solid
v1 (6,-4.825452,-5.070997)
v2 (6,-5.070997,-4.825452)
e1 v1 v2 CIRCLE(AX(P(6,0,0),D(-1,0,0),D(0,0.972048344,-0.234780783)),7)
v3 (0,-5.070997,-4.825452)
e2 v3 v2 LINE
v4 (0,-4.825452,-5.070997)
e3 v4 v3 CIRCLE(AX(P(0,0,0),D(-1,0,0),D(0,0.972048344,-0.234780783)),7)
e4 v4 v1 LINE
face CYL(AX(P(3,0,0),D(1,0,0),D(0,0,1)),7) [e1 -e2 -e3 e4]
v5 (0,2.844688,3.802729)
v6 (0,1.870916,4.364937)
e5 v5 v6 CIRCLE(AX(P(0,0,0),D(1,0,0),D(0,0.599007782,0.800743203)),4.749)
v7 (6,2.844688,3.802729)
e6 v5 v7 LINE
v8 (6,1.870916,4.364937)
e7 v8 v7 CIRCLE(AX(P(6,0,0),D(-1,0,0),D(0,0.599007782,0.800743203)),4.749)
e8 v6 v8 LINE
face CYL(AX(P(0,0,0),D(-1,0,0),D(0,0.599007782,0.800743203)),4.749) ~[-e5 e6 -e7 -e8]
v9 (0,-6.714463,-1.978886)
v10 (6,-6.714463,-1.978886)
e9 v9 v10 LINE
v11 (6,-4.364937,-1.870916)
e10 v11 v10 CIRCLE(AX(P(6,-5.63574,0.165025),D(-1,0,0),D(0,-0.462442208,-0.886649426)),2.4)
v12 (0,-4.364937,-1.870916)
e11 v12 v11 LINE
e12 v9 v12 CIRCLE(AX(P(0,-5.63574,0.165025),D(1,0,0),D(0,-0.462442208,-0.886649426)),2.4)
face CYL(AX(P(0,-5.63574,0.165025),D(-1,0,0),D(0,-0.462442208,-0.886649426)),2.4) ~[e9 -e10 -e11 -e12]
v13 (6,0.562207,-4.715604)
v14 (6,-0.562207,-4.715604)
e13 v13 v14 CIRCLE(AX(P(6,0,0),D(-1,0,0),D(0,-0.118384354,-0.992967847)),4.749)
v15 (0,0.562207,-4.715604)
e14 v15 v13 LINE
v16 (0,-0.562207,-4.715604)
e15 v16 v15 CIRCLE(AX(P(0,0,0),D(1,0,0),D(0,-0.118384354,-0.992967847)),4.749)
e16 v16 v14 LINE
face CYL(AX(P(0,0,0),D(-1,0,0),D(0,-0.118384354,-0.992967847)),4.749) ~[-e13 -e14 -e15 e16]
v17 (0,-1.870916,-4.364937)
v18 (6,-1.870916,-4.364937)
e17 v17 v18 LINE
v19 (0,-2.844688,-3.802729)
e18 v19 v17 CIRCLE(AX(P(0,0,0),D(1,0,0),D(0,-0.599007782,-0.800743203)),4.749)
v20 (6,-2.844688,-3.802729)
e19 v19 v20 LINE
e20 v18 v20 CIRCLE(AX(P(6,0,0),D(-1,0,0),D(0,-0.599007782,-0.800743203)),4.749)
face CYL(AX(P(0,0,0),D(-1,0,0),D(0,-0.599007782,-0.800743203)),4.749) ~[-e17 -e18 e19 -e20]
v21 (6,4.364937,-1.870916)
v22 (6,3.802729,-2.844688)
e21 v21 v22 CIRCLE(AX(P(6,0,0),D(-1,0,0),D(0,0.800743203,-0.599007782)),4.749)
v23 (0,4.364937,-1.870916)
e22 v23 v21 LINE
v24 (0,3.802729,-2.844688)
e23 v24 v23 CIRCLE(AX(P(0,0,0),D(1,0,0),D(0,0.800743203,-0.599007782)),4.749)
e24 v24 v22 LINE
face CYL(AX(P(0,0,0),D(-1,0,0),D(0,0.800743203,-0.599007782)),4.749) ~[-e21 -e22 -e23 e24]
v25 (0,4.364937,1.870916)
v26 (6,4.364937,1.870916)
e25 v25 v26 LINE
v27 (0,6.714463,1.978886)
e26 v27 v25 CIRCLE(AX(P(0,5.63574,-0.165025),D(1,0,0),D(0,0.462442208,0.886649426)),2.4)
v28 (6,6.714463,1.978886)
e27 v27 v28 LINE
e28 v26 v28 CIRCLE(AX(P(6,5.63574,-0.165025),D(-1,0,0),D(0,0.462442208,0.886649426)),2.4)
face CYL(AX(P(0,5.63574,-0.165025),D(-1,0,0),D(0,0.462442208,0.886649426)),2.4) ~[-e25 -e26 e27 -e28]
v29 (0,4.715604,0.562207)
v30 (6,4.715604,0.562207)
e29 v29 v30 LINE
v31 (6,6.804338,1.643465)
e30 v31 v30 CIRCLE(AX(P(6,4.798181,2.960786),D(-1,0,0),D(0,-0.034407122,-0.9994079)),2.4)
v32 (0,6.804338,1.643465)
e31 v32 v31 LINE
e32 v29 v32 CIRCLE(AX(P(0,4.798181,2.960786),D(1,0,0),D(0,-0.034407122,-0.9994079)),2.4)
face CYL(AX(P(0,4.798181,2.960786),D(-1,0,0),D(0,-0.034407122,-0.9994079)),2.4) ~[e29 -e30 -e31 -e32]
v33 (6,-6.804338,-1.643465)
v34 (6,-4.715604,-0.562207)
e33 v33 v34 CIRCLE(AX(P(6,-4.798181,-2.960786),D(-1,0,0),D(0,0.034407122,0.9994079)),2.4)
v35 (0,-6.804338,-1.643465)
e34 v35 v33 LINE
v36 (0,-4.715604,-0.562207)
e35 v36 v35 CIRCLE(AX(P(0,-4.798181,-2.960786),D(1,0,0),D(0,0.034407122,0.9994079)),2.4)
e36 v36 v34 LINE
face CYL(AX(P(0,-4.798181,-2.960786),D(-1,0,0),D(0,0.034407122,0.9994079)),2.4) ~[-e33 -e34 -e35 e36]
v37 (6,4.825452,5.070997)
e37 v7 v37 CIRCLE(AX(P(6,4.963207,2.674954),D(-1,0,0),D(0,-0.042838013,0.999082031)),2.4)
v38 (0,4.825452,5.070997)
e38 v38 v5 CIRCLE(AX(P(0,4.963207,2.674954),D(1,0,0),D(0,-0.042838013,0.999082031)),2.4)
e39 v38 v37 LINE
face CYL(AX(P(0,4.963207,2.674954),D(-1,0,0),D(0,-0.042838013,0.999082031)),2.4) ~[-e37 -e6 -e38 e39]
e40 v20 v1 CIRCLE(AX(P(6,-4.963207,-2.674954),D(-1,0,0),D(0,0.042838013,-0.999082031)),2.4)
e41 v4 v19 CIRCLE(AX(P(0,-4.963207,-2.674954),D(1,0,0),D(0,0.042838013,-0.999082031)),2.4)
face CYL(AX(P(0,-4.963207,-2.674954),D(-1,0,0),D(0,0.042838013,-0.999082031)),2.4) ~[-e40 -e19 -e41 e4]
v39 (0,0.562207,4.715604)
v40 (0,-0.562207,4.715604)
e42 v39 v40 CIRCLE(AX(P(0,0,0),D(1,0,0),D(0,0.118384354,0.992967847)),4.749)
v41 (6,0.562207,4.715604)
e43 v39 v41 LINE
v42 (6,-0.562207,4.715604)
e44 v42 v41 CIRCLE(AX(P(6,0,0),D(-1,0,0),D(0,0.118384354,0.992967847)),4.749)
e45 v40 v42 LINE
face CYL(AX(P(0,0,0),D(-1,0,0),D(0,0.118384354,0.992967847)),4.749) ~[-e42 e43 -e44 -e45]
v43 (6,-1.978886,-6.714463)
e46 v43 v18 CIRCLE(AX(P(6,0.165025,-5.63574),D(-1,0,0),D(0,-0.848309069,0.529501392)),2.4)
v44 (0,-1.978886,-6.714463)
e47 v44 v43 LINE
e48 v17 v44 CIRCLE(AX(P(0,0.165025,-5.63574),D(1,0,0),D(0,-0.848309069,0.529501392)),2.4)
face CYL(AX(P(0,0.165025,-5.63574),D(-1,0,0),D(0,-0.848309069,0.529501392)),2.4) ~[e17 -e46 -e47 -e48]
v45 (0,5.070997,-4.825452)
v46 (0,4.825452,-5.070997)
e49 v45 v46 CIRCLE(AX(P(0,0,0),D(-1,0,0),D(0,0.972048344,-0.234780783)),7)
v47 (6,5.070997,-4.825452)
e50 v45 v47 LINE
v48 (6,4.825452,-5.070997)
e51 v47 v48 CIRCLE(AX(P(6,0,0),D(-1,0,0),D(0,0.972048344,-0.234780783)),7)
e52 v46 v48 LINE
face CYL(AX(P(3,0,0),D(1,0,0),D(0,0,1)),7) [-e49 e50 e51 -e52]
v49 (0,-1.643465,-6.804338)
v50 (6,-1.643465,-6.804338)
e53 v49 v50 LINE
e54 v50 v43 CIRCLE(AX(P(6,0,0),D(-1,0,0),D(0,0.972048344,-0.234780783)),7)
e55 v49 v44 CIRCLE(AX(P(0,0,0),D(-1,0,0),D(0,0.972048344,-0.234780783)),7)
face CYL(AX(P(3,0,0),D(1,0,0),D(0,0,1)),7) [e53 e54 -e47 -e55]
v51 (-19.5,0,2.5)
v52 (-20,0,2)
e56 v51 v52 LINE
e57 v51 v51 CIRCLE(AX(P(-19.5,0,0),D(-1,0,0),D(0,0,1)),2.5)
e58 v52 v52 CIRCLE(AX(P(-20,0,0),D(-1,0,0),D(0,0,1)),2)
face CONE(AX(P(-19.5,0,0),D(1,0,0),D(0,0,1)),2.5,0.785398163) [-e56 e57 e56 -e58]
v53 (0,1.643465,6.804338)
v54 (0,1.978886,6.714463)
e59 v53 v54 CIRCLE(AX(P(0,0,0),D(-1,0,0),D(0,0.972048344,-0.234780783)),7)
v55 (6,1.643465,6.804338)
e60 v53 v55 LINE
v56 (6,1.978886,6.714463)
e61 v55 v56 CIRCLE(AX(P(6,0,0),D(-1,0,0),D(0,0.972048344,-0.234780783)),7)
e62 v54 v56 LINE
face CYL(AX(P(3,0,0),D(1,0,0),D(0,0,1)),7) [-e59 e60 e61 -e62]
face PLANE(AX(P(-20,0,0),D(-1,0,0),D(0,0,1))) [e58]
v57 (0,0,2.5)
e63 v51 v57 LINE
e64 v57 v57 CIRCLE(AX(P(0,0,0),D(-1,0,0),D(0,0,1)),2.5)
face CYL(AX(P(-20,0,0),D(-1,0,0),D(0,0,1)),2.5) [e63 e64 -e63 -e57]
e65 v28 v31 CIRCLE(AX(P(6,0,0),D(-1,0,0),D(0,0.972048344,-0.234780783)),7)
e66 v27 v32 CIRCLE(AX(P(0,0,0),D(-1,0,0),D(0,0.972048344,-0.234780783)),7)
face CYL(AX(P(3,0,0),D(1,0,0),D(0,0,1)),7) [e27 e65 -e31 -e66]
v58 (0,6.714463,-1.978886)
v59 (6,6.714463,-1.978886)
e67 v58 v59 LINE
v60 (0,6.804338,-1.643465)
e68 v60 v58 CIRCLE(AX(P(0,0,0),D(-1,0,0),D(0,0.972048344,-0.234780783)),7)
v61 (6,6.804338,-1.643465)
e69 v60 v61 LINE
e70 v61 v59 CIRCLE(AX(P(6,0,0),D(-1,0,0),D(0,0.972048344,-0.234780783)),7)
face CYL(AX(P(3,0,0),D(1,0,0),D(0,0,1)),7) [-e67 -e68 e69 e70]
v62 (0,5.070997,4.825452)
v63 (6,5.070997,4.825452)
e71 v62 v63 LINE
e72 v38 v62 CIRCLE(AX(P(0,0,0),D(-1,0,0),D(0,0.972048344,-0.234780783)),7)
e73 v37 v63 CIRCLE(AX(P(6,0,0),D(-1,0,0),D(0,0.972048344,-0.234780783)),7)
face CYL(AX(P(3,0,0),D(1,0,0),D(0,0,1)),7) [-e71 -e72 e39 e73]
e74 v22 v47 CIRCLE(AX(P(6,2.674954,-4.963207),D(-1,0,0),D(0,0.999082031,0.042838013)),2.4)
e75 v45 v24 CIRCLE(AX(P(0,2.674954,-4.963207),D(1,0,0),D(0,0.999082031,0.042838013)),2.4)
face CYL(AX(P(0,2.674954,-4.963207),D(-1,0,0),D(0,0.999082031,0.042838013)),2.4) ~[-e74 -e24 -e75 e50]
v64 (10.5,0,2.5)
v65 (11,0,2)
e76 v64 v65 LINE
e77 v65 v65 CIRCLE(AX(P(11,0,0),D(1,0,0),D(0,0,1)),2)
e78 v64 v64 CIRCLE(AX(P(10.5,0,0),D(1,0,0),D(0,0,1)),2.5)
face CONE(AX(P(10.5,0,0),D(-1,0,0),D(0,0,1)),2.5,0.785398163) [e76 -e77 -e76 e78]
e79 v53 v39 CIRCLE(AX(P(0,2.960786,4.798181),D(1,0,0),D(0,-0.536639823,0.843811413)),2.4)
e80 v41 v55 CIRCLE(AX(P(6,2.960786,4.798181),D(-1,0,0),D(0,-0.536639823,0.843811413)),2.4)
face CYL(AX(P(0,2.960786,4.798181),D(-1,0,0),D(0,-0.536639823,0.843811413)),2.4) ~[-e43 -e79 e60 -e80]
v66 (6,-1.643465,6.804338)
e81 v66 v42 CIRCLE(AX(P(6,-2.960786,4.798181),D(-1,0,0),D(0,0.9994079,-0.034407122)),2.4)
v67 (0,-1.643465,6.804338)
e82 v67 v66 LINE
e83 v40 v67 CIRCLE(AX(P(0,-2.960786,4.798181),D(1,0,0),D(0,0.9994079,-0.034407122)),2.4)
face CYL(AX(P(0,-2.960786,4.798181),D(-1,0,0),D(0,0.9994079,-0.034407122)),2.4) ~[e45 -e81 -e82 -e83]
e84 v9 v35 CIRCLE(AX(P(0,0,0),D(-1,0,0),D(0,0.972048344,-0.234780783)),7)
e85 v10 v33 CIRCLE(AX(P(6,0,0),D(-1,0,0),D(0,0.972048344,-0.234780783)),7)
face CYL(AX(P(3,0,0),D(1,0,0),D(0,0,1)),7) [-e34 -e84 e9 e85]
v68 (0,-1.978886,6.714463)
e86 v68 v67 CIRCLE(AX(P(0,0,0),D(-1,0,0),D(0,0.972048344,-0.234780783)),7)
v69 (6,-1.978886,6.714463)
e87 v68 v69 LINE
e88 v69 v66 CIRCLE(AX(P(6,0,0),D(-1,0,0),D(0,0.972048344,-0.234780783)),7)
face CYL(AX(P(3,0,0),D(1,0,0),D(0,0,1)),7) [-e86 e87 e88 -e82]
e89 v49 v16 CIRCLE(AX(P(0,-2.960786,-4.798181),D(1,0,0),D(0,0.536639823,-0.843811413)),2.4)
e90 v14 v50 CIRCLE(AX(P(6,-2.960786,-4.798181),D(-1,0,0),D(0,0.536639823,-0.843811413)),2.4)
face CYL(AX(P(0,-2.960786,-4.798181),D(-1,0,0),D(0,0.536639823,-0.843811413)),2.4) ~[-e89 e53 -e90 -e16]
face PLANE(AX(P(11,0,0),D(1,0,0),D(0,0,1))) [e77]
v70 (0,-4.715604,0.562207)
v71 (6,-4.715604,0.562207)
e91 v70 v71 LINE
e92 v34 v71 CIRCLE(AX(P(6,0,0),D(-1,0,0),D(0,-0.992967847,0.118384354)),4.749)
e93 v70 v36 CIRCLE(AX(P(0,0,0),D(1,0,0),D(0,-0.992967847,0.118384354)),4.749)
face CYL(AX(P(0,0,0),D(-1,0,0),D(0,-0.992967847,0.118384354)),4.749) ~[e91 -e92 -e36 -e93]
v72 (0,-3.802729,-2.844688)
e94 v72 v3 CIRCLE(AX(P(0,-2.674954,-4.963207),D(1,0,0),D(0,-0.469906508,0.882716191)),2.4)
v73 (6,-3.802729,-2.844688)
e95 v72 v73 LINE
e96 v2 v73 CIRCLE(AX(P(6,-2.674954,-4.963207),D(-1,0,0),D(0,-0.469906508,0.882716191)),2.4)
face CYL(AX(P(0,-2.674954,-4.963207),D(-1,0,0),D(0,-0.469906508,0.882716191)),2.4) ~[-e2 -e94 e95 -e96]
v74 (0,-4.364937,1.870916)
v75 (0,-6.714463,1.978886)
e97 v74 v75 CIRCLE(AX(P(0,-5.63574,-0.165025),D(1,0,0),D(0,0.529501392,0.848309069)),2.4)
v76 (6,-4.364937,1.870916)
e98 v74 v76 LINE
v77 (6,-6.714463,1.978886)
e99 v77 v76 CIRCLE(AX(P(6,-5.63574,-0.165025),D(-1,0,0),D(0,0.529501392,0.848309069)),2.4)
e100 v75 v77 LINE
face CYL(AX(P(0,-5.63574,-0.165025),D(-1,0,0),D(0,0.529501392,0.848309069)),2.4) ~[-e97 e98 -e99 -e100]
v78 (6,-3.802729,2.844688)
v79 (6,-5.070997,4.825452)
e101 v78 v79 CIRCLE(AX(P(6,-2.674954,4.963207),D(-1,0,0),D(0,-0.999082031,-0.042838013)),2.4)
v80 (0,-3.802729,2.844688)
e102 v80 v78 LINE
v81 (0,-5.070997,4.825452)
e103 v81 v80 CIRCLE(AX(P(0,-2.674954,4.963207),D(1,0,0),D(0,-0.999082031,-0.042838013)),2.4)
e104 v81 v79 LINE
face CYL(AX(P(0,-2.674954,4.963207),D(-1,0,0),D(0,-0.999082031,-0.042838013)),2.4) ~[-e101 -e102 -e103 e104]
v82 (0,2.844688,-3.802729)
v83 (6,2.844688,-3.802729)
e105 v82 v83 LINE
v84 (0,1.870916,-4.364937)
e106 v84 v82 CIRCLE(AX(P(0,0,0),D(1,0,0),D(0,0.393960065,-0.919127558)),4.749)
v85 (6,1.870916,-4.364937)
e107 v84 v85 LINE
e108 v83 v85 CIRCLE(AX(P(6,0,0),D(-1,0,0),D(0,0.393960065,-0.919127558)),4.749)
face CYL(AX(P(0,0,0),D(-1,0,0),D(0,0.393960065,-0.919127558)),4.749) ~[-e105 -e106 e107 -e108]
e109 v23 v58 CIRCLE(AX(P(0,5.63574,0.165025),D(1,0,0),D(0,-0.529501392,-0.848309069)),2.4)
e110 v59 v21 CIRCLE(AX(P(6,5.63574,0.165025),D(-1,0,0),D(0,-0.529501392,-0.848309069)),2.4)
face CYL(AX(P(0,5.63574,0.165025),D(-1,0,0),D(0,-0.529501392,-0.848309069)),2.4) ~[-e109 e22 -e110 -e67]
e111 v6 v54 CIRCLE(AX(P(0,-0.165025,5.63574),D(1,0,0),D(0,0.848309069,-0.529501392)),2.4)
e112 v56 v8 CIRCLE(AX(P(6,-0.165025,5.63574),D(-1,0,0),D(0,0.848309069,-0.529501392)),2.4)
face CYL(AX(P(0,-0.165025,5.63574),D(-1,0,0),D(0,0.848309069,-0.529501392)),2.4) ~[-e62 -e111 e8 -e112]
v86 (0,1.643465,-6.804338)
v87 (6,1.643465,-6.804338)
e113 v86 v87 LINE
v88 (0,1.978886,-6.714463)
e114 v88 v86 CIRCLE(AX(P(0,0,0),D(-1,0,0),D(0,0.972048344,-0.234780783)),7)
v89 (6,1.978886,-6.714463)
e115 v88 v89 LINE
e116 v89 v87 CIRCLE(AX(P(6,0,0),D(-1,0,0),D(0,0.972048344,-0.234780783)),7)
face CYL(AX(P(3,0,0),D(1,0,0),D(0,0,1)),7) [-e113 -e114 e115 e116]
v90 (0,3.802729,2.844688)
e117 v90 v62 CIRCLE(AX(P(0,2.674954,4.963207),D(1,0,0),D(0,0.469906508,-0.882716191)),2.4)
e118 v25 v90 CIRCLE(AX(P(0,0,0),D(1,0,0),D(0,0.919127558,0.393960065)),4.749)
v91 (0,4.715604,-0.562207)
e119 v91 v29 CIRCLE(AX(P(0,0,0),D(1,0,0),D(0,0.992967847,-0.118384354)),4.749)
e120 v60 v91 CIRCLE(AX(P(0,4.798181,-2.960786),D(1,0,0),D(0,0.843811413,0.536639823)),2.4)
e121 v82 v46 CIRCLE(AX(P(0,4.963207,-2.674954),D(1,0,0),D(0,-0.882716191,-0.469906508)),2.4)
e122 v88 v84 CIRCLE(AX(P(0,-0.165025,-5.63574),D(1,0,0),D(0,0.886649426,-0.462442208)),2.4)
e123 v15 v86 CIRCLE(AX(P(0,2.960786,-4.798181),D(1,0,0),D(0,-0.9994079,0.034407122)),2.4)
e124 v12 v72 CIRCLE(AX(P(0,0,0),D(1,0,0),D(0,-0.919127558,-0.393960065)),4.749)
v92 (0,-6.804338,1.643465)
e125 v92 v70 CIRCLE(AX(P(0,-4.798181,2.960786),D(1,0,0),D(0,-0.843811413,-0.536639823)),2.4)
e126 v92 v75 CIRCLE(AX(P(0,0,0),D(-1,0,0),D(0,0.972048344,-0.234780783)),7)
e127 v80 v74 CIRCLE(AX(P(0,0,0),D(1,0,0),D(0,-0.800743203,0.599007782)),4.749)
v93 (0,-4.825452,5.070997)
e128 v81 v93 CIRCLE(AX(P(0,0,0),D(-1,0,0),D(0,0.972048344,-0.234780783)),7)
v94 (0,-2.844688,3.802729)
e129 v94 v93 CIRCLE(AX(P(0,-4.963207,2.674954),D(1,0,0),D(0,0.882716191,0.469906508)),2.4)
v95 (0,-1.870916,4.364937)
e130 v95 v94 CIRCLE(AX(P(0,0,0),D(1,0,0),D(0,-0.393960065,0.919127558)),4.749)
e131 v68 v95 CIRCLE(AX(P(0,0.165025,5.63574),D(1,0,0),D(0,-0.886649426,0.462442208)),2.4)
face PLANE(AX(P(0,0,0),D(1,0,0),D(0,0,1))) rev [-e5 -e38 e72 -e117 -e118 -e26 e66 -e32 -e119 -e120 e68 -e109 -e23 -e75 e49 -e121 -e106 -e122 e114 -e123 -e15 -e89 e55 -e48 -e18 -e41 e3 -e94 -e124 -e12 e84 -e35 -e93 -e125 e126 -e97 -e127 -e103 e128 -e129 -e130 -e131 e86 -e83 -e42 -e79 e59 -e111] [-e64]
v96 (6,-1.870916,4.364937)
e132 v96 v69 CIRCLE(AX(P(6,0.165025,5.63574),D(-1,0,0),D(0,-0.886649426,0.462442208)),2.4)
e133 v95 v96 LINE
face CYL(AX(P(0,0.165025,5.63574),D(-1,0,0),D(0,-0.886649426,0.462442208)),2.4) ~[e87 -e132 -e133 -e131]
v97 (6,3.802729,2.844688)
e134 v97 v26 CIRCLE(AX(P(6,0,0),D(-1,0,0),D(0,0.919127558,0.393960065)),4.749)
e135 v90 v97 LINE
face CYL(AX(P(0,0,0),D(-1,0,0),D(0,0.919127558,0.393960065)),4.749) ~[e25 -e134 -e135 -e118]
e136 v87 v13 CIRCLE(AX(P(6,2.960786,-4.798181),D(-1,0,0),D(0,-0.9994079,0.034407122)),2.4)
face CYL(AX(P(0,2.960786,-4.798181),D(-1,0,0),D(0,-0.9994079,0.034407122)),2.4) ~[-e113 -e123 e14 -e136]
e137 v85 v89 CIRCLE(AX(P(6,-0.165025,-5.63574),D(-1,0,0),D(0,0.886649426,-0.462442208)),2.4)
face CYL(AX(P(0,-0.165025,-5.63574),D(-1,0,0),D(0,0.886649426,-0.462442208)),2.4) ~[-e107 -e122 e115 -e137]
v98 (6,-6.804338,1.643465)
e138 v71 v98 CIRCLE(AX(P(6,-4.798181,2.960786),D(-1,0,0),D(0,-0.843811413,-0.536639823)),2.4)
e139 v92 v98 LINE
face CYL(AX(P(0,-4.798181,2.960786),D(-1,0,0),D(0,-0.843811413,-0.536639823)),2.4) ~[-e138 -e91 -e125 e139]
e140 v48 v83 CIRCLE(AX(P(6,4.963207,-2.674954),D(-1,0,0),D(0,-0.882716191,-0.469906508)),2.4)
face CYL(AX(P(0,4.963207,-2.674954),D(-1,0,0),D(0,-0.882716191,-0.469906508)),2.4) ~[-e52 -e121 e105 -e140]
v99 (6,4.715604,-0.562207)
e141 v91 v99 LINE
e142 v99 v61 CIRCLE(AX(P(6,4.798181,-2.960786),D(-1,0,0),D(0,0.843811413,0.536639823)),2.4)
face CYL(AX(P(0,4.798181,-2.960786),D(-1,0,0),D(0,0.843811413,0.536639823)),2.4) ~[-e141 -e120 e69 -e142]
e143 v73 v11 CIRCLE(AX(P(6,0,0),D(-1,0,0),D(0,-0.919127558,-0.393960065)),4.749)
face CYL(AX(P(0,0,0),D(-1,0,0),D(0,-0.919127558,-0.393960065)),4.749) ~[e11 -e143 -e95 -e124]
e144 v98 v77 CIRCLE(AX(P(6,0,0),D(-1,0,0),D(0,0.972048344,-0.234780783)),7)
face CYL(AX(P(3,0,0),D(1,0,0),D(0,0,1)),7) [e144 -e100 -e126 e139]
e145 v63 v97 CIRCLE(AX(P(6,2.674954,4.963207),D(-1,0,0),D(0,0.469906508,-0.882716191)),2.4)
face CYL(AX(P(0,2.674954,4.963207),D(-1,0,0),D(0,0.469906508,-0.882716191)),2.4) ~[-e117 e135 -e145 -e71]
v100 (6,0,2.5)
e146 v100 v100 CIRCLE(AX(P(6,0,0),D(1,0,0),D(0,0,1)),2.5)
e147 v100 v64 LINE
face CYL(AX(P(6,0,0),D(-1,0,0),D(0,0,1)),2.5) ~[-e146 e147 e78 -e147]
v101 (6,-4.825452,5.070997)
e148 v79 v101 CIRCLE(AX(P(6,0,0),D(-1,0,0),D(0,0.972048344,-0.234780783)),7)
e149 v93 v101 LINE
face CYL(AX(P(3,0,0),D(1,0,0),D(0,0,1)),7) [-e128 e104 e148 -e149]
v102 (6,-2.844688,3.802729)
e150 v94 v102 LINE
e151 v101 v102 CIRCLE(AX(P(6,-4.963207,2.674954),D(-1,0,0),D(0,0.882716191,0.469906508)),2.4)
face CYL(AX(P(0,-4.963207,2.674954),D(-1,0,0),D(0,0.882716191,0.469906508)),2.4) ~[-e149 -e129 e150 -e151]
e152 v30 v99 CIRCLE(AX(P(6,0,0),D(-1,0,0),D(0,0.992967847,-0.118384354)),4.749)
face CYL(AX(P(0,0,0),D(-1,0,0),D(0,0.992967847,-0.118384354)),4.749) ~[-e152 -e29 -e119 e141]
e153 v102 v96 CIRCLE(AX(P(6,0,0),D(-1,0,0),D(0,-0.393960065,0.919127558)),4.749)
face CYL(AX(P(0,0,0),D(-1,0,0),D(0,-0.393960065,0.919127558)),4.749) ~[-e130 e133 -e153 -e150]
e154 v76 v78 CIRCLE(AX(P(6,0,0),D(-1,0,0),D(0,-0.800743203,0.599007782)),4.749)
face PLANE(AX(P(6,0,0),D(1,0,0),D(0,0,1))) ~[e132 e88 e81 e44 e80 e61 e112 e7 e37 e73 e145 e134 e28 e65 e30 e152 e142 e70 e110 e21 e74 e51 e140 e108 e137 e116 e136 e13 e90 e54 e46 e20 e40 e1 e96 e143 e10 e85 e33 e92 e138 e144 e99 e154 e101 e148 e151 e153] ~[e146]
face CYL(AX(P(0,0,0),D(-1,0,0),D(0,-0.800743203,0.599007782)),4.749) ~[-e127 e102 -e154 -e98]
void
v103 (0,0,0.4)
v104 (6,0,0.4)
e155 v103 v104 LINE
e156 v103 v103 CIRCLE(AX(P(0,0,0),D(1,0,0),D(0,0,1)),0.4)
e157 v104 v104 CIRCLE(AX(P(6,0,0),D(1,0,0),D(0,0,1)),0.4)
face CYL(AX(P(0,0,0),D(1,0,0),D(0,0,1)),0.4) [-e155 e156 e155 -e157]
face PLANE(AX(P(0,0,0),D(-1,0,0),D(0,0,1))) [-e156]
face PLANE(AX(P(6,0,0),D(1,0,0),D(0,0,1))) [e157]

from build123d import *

# Parameters (mm, degrees)
BASPROSKE_W         = 6
BASPROSKE_H         = 7
TOOTHCUT_DEPTH      = 12.575836903
TEETHCUTS_COUNT     = 12
TEETHCUTS_ANGLE     = 330
BORSKE_R            = 0.4
BORE_DEPTH          = 50.0000508
SKETCH1_R           = 2.5
BOSS_EXTRUDE1_DEPTH = 5
BOSS_EXTRUDE2_START = 20
SKETCH2_R           = 2.5
BOSS_EXTRUDE2_DEPTH = 20
CHAMFER1_SIZE       = 0.5


with BuildPart() as part:
    # BasProSke → Base-Revolve (revolve)
    with BuildSketch(Plane(origin=(0, 0, 0), x_dir=(1, 0, 0), z_dir=(0, 1, 0)), mode=Mode.PRIVATE) as base_revolve_sk:
        with Locations((3, 3.5)):
            Rectangle(BASPROSKE_W, BASPROSKE_H)
    revolve(base_revolve_sk.sketch.rotate(Axis((-10, 0, 0), (1, 0, 0)), 180), axis=Axis((-10, 0, 0), (1, 0, 0)))

    # TooCutSke → ToothCut (cut, through all)
    with BuildSketch(Plane(origin=(0, 0, 0), x_dir=(0, 0, -1), z_dir=(1, 0, 0))):
        with BuildLine():
            ThreePointArc((0.562207301, 4.715604304), (0, 4.749), (-0.562207301, 4.715604304))
            ThreePointArc((-0.562207301, 4.715604304), (-0.837528627, 5.917009812), (-1.672850686, 6.823328788))
            ThreePointArc((-1.672850686, 6.823328788), (0, 7.0254), (1.672850686, 6.823328788))
            ThreePointArc((1.672850686, 6.823328788), (0.837528627, 5.917009812), (0.562207301, 4.715604304))
        make_face()
    toothcut = extrude(amount=TOOTHCUT_DEPTH, mode=Mode.SUBTRACT)

    # TeethCuts: ToothCut ×12 about axis
    teethcuts_axis = Axis((-10, 0, 0), (1, 0, 0))
    for i in range(1, TEETHCUTS_COUNT):
        add(toothcut.rotate(teethcuts_axis, i * TEETHCUTS_ANGLE / (TEETHCUTS_COUNT - 1)), mode=Mode.SUBTRACT)

    # BorSke → Bore (cut, symmetric)
    with BuildSketch(Plane(origin=(0, 0, 0), x_dir=(0, 0, -1), z_dir=(1, 0, 0))):
        with Locations(Location((0, 0, 0), (0, 0, 180))):
            Circle(BORSKE_R)
    extrude(amount=BORE_DEPTH, both=True, mode=Mode.SUBTRACT)

    # Sketch1 → Boss-Extrude1 (add)
    with BuildSketch(Plane(origin=(6, 0, 0), x_dir=(0, 0, -1), z_dir=(1, 0, 0))):
        with Locations(Location((0, 0, 0), (0, 0, 180))):
            Circle(SKETCH1_R)
    extrude(amount=BOSS_EXTRUDE1_DEPTH)

    # Sketch2 → Boss-Extrude2 (add)
    with BuildSketch(Plane.ZY.offset(BOSS_EXTRUDE2_START)):
        Circle(SKETCH2_R)
    extrude(amount=-BOSS_EXTRUDE2_DEPTH)

    # Chamfer1
    chamfer1_edges = [part.edges().sort_by_distance(p)[0] for p in [
        (11, 0, -2.5),
        (-20, 0, -2.5),
    ]]
    chamfer(chamfer1_edges, length=CHAMFER1_SIZE)


solid = part.part
